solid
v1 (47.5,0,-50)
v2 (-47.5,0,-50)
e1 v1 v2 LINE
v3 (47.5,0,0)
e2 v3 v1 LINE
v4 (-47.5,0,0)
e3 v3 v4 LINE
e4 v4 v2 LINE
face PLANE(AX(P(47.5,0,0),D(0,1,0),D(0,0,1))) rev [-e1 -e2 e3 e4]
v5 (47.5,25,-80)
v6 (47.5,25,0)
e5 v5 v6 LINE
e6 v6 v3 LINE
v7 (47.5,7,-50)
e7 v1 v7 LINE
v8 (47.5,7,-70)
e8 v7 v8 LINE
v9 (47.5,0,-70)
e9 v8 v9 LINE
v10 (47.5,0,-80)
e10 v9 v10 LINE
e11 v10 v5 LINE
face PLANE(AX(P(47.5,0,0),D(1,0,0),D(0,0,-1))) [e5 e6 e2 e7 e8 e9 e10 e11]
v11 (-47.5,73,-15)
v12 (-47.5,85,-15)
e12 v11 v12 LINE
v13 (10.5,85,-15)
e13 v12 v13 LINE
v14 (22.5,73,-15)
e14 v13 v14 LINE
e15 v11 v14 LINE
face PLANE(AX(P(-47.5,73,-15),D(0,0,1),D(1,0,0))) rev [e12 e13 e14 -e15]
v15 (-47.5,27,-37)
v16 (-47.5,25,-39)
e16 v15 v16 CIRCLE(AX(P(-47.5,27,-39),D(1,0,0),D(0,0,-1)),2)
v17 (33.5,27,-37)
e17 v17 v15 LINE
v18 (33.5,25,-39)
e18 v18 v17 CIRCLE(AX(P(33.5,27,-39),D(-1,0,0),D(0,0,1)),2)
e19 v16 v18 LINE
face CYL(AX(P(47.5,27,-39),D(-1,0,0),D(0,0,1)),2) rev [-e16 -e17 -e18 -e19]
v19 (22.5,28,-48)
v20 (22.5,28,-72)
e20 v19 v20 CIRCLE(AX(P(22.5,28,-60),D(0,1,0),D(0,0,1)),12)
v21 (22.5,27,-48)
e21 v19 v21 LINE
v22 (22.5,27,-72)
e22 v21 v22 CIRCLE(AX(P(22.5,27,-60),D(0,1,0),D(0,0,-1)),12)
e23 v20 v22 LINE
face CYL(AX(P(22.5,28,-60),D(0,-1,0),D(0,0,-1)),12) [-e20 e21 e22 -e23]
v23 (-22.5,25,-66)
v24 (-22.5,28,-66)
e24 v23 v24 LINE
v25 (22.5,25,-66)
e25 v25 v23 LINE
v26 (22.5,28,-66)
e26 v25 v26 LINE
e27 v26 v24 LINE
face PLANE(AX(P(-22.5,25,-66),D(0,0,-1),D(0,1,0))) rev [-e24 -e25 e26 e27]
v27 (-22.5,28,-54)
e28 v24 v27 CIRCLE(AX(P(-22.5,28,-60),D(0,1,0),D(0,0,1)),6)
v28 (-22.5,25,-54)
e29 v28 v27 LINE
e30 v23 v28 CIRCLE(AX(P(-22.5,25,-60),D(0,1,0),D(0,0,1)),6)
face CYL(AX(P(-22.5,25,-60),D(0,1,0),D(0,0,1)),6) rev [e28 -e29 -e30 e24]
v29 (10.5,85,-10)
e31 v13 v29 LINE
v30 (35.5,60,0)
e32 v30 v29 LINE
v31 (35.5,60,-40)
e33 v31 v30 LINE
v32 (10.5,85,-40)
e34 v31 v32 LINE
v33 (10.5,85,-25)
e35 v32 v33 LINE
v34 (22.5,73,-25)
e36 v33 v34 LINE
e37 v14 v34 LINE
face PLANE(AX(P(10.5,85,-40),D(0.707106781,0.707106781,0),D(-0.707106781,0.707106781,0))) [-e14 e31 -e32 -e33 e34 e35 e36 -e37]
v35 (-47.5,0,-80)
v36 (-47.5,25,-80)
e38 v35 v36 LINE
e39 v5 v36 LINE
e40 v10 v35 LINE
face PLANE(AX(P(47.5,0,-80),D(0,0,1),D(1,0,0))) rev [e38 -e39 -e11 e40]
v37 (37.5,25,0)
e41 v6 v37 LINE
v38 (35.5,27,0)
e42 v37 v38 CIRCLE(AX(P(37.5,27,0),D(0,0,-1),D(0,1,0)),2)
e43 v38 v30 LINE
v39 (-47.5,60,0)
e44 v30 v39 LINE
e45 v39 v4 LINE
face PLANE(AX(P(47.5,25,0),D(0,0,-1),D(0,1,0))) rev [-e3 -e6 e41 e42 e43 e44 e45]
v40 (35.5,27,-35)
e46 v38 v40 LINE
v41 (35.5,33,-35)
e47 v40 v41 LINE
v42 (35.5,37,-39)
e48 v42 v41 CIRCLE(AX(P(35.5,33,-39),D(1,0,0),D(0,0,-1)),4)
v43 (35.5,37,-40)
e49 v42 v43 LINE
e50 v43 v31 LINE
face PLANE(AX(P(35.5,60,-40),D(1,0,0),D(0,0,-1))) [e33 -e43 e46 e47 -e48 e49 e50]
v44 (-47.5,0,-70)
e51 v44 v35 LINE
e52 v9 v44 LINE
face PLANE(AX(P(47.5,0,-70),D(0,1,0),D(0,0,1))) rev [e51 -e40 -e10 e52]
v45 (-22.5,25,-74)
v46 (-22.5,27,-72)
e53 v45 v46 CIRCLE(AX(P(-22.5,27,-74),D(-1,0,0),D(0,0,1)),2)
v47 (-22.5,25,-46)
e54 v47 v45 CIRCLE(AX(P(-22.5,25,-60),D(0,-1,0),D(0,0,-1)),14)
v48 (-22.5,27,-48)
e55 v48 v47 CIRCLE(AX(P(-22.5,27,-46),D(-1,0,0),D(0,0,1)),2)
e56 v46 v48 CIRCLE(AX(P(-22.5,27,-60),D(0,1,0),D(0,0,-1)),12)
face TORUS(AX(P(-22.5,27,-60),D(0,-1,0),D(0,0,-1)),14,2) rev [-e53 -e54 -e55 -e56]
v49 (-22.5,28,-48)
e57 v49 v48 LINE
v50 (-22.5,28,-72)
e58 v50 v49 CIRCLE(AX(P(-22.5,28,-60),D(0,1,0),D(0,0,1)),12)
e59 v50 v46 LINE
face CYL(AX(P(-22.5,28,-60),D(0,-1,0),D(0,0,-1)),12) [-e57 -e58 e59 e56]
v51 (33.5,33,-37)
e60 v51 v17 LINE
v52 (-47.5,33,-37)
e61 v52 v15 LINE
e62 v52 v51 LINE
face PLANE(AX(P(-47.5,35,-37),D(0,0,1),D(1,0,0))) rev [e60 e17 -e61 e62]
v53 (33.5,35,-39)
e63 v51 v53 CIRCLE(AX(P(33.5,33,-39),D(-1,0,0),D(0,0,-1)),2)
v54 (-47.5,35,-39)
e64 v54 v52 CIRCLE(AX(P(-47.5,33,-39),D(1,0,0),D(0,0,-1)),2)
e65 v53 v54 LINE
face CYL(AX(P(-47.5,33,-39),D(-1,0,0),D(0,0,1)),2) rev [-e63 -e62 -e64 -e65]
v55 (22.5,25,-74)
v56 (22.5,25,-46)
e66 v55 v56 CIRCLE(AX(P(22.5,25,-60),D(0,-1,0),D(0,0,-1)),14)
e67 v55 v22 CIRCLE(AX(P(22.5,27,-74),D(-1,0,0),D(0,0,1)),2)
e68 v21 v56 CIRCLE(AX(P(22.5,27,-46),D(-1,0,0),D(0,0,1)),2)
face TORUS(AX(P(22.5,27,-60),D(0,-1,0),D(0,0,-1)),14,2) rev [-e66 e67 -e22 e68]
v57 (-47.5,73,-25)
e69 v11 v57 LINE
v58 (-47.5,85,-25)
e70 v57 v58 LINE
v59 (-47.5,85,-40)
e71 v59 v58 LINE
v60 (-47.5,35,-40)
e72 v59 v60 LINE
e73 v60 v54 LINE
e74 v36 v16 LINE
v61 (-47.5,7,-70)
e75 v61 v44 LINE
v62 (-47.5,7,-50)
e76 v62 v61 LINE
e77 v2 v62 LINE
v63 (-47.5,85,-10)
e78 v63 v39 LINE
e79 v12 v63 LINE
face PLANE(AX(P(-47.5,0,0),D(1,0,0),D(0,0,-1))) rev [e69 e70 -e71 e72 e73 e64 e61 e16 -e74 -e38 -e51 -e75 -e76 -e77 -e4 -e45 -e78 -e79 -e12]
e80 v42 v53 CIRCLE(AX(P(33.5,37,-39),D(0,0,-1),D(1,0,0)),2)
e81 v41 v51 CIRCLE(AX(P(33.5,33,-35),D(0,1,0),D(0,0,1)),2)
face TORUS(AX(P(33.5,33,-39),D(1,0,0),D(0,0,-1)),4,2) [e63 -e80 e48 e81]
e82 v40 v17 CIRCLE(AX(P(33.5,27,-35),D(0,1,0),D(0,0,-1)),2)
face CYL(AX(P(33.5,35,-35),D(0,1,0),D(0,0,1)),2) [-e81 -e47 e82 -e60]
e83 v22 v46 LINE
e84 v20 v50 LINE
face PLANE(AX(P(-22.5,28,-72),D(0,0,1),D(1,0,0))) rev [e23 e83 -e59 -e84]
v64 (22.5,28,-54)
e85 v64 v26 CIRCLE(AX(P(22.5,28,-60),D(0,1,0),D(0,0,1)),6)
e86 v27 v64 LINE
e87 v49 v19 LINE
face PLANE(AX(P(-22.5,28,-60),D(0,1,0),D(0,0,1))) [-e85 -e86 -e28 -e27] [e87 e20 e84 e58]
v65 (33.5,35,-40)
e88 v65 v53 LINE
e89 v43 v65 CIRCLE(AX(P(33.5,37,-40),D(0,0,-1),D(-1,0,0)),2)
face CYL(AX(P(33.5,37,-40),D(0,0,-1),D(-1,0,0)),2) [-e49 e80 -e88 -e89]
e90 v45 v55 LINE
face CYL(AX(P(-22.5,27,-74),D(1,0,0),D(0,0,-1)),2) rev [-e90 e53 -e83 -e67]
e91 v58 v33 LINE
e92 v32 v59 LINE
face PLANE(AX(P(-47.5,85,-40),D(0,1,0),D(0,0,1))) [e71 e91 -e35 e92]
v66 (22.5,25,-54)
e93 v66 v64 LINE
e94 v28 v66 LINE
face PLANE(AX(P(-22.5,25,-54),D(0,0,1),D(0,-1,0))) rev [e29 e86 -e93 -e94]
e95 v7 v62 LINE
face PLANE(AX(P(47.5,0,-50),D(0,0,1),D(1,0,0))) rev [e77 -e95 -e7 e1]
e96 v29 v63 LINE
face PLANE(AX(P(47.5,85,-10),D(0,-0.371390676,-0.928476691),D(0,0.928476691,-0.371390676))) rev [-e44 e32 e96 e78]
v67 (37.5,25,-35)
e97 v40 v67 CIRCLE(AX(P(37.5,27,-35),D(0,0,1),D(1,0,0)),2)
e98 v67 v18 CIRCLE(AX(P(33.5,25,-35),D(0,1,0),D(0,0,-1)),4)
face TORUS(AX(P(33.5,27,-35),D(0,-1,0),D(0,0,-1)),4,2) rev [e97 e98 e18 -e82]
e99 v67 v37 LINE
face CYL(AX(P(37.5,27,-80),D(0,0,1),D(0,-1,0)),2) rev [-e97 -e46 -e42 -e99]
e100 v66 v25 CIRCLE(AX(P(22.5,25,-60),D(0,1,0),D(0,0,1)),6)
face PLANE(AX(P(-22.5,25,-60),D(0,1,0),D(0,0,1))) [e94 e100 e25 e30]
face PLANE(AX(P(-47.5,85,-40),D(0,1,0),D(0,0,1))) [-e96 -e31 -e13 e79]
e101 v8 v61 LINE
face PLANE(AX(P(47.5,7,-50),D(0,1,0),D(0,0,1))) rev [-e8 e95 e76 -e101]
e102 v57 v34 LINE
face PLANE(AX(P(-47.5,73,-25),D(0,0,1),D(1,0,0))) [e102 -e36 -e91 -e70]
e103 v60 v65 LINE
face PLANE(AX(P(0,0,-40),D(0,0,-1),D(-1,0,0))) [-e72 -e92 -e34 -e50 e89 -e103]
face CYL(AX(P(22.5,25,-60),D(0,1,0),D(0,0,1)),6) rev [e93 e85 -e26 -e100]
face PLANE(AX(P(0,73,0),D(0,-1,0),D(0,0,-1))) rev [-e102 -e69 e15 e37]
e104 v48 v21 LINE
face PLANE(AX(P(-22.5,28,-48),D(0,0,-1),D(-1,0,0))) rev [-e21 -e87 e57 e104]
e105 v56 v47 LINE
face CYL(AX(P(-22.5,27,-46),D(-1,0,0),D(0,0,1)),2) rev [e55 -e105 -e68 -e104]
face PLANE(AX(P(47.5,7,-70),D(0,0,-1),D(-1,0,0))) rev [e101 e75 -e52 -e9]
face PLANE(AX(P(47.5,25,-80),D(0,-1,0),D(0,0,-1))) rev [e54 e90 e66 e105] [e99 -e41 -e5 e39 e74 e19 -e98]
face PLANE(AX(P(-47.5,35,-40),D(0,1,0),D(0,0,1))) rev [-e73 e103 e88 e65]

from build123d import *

# Parameters (mm, degrees)
BASE_BLOCK_95_DEPTH      = 47.5
UPRIGHT_BLOCK_40_DEPTH   = 40
RELIEF_GROOVE_SKETCH_W   = 3
RELIEF_GROOVE_SKETCH_H   = 10
RELIEF_GROOVE_3X10_DEPTH = 144.227092409
UPRIGHT_FILLET_R2_R      = 2
TOP_SLOT_SKETCH_W        = 71
TOP_SLOT_SKETCH_H        = 10
TOP_SLOT_10_WIDE_DEPTH   = 12
V_NOTCH_DEPTH            = 151.499169433
RAISED_PAD_3MM_DEPTH     = 3
PAD_FILLET_R2_R          = 2
PAD_U_SLOT_12_WIDE_DEPTH = 3


with BuildPart() as part:
    # Base Profile Sketch → Base Block 95 (new, symmetric)
    with BuildSketch(Plane(origin=(0, 0, 0), x_dir=(0, 0, -1), z_dir=(1, 0, 0))):
        Polygon((0, 0), (50, 0), (50, 7), (70, 7), (70, 0), (80, 0), (80, 25), (0, 25), align=None)
    extrude(amount=BASE_BLOCK_95_DEPTH, both=True)

    # Upright Profile Sketch → Upright Block 40 (add)
    with BuildSketch(Plane.XY):
        Polygon((-47.5, 25), (-47.5, 85), (10.5, 85), (35.5, 60), (35.5, 25), align=None)
    extrude(amount=-UPRIGHT_BLOCK_40_DEPTH)

    # Relief Groove Sketch → Relief Groove 3x10 (cut, through all)
    with BuildSketch(Plane(origin=(35.5, 0, 0), x_dir=(0, 0, -1), z_dir=(1, 0, 0))):
        with Locations((38.5, 30)):
            Rectangle(RELIEF_GROOVE_SKETCH_W, RELIEF_GROOVE_SKETCH_H)
    extrude(amount=-RELIEF_GROOVE_3X10_DEPTH, mode=Mode.SUBTRACT)

    # Upright Fillet R2
    upright_fillet_r2_edges = [part.edges().sort_by_distance(p)[0] for p in [
        (35.5, 25, -18.5),
        (-6, 25, -37),
        (-6, 35, -37),
        (35.5, 35, -38.5),
        (35.5, 30, -37),
    ]]
    fillet(upright_fillet_r2_edges, radius=UPRIGHT_FILLET_R2_R)

    # Top Slot Sketch → Top Slot 10 Wide (cut)
    with BuildSketch(Plane(origin=(0, 85, 0), x_dir=(1, 0, 0), z_dir=(0, 1, 0))):
        with Locations((-12, 20)):
            Rectangle(TOP_SLOT_SKETCH_W, TOP_SLOT_SKETCH_H)
    extrude(amount=-TOP_SLOT_10_WIDE_DEPTH, mode=Mode.SUBTRACT)

    # V Notch Sketch → V Notch (cut, through all)
    with BuildSketch(Plane.ZY.offset(47.5)):
        Polygon((0, 60), (0, 85), (-10, 85), align=None)
    extrude(amount=-V_NOTCH_DEPTH, mode=Mode.SUBTRACT)

    # Raised Pad Sketch → Raised Pad 3mm (add)
    with BuildSketch(Plane(origin=(0, 25, 0), x_dir=(1, 0, 0), z_dir=(0, 1, 0))):
        with BuildLine():
            Line((-22.5, 72), (22.5, 72))
            ThreePointArc((22.5, 72), (34.5, 60), (22.5, 48))
            Line((22.5, 48), (-22.5, 48))
            ThreePointArc((-22.5, 48), (-34.5, 60), (-22.5, 72))
        make_face()
    extrude(amount=RAISED_PAD_3MM_DEPTH)

    # Pad Fillet R2
    pad_fillet_r2_edges = [part.edges().sort_by_distance(p)[0] for p in [
        (-34.5, 25, -60),
        (0, 25, -48),
        (34.5, 25, -60),
        (0, 25, -72),
    ]]
    fillet(pad_fillet_r2_edges, radius=PAD_FILLET_R2_R)

    # Pad Slot Sketch → Pad U-Slot 12 Wide (cut)
    with BuildSketch(Plane(origin=(0, 28, 0), x_dir=(1, 0, 0), z_dir=(0, 1, 0))):
        with BuildLine():
            Line((-22.5, 66), (22.5, 66))
            ThreePointArc((22.5, 66), (28.5, 60), (22.5, 54))
            Line((22.5, 54), (-22.5, 54))
            ThreePointArc((-22.5, 54), (-28.5, 60), (-22.5, 66))
        make_face()
    extrude(amount=-PAD_U_SLOT_12_WIDE_DEPTH, mode=Mode.SUBTRACT)


solid = part.part
